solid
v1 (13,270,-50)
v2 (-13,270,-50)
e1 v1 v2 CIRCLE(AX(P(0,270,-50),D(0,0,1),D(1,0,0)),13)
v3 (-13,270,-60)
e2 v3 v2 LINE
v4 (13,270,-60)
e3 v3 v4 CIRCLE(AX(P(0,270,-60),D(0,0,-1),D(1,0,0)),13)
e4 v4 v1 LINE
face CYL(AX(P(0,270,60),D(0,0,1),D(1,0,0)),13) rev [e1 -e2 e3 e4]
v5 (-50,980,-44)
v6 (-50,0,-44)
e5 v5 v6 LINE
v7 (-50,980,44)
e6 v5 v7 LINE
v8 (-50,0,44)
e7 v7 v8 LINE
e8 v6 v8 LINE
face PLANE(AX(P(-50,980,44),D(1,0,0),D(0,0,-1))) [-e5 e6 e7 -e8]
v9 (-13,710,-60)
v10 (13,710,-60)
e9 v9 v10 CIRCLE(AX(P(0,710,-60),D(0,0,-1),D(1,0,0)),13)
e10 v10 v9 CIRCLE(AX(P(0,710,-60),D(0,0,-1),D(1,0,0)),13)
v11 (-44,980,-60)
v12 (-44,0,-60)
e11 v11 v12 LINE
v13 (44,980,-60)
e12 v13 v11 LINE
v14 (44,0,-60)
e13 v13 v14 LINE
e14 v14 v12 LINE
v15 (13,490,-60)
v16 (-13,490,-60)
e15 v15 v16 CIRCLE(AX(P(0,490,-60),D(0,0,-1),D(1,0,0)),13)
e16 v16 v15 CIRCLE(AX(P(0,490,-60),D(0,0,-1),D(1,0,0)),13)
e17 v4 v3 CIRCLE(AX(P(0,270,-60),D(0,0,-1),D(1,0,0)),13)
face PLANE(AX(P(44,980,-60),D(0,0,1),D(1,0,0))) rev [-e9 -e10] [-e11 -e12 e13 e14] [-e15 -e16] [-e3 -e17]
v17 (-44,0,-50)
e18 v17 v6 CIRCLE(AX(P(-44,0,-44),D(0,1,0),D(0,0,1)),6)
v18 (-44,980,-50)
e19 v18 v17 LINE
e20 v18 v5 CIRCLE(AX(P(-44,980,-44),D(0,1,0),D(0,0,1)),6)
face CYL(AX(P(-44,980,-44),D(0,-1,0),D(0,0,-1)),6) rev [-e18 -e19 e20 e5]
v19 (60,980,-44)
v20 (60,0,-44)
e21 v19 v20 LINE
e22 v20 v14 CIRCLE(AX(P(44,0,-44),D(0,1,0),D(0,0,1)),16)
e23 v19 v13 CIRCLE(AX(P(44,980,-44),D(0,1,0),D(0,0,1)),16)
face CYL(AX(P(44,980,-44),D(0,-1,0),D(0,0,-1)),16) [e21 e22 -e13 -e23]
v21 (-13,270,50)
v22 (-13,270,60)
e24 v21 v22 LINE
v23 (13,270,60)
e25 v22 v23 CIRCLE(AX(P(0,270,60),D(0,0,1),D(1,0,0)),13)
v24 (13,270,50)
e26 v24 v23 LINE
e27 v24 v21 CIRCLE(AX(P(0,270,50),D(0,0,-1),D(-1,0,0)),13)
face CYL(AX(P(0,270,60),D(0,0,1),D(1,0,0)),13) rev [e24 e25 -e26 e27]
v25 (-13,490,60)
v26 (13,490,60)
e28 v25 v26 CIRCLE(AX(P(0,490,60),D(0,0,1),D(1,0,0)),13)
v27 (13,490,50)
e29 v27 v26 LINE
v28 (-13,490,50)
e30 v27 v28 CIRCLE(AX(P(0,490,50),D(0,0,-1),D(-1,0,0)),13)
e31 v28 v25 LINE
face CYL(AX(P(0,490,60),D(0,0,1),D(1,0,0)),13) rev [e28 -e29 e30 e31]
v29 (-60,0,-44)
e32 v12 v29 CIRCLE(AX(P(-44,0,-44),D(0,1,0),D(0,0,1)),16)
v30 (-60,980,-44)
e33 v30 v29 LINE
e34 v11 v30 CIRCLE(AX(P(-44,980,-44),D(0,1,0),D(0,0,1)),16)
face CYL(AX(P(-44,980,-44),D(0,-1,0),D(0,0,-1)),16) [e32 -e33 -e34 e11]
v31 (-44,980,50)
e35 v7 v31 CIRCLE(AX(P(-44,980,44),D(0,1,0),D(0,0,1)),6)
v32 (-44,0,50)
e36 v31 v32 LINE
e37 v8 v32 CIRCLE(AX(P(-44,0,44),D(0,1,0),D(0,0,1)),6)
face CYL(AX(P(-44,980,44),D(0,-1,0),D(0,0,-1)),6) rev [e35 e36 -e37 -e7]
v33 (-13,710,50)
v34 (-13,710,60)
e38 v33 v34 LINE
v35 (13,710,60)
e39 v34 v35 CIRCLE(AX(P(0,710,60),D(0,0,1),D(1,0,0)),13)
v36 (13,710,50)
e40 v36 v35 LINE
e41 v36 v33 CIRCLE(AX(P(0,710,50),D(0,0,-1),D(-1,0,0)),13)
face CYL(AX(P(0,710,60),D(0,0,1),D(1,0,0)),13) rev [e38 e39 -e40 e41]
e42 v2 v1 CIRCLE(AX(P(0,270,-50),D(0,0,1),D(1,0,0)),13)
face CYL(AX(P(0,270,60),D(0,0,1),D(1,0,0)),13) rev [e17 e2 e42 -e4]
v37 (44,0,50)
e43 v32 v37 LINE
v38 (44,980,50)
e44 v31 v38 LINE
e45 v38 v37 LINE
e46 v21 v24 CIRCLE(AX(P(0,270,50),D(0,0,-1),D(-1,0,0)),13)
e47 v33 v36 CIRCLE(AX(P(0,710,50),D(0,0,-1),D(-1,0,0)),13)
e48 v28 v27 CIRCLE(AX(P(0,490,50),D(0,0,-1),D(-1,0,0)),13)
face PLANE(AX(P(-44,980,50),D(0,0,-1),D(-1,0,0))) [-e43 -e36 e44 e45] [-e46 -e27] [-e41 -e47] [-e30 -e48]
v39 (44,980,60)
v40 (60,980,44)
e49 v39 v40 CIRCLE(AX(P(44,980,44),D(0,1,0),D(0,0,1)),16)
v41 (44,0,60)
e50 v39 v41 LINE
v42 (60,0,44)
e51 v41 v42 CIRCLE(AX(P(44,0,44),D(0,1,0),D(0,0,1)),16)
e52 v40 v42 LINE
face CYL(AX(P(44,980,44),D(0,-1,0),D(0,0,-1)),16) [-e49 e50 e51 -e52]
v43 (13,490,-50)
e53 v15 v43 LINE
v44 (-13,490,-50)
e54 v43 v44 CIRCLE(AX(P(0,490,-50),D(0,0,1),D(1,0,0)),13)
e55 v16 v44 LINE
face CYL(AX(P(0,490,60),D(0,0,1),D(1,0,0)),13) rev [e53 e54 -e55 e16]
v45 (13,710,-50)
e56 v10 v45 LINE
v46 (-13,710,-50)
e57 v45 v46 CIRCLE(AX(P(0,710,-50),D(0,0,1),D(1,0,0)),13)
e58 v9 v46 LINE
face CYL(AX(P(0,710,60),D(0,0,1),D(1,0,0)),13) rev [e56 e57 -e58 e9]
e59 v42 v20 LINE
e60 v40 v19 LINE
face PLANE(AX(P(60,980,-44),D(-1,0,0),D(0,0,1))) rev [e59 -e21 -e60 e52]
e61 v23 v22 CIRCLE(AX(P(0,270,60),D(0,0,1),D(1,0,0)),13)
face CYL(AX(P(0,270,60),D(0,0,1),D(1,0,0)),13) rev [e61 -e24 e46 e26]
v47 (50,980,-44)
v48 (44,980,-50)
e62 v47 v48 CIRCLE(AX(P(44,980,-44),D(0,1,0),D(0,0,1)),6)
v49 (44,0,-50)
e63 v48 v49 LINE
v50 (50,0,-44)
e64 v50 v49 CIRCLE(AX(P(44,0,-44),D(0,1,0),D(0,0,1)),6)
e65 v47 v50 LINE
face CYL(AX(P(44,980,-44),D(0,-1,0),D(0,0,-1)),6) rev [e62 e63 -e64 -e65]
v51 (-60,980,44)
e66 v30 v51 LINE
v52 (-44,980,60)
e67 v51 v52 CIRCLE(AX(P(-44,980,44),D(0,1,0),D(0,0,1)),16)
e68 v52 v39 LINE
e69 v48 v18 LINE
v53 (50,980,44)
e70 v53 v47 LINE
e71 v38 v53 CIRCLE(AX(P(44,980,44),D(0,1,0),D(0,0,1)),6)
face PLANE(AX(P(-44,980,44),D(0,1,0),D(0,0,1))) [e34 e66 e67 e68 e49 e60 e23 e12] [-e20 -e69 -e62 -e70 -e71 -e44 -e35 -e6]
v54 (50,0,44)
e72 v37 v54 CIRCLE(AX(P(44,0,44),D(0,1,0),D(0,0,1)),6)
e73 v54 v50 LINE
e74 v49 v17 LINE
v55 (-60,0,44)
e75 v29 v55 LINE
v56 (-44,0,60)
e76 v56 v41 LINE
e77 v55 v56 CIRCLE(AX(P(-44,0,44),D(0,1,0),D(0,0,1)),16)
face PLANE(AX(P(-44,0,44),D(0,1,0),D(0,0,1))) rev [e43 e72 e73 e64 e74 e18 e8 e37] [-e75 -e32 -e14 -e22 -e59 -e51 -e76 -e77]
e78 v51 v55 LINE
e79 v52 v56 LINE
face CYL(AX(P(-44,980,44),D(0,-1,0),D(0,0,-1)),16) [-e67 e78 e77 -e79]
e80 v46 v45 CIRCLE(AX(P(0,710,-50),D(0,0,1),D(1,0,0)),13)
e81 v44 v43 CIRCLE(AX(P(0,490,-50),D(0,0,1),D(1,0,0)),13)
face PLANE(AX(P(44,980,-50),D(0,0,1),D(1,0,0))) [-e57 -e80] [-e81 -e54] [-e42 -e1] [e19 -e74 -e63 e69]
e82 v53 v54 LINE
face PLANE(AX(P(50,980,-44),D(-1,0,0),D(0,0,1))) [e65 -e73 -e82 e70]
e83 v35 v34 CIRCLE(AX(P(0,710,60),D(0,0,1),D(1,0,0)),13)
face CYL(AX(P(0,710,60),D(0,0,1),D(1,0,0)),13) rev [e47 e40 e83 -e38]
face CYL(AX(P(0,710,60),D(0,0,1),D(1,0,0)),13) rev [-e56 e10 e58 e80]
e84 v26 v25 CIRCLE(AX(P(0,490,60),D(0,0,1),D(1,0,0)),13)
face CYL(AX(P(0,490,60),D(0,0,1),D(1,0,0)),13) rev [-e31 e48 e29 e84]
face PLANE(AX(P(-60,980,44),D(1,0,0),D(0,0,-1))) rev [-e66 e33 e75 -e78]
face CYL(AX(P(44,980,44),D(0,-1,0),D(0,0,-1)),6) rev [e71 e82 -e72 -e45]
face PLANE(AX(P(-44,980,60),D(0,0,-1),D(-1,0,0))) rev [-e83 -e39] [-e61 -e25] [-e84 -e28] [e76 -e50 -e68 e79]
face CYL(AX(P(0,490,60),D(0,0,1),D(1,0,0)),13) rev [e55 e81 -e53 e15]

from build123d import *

# Parameters (mm, degrees)
GB_T6728_2002_120_120_10_1_DEPTH = 980
HOLE_WIZARD_26_1_D               = 26


with BuildPart() as part:
    # Sketch12 → 结构用冷弯空心方钢(gb t6728-2002) 120×120×10(1) (new body)
    with BuildSketch(Plane(origin=(0, 0, 0), x_dir=(-1, 0, 0), z_dir=(0, 1, 0))):
        with BuildLine():
            Line((-44, -60), (44, -60))
            ThreePointArc((44, -60), (55.313708499, -55.313708499), (60, -44))
            Line((60, -44), (60, 44))
            ThreePointArc((60, 44), (55.313708499, 55.313708499), (44, 60))
            Line((44, 60), (-44, 60))
            ThreePointArc((-44, 60), (-55.313708499, 55.313708499), (-60, 44))
            Line((-60, 44), (-60, -44))
            ThreePointArc((-60, -44), (-55.313708499, -55.313708499), (-44, -60))
        make_face()
        with BuildLine():
            Line((-44, -50), (44, -50))
            ThreePointArc((44, -50), (48.242640687, -48.242640687), (50, -44))
            Line((50, -44), (50, 44))
            ThreePointArc((50, 44), (48.242640687, 48.242640687), (44, 50))
            Line((44, 50), (-44, 50))
            ThreePointArc((-44, 50), (-48.242640687, 48.242640687), (-50, 44))
            Line((-50, 44), (-50, -44))
            ThreePointArc((-50, -44), (-48.242640687, -48.242640687), (-44, -50))
        make_face(mode=Mode.SUBTRACT)
    extrude(amount=GB_T6728_2002_120_120_10_1_DEPTH)

    # Ø26 直径孔1 (through all)
    with Locations(Plane.XY.offset(60)):
        with Locations((0, 710), (0, 490), (0, 270)):
            Hole(HOLE_WIZARD_26_1_D / 2)


solid = part.part
